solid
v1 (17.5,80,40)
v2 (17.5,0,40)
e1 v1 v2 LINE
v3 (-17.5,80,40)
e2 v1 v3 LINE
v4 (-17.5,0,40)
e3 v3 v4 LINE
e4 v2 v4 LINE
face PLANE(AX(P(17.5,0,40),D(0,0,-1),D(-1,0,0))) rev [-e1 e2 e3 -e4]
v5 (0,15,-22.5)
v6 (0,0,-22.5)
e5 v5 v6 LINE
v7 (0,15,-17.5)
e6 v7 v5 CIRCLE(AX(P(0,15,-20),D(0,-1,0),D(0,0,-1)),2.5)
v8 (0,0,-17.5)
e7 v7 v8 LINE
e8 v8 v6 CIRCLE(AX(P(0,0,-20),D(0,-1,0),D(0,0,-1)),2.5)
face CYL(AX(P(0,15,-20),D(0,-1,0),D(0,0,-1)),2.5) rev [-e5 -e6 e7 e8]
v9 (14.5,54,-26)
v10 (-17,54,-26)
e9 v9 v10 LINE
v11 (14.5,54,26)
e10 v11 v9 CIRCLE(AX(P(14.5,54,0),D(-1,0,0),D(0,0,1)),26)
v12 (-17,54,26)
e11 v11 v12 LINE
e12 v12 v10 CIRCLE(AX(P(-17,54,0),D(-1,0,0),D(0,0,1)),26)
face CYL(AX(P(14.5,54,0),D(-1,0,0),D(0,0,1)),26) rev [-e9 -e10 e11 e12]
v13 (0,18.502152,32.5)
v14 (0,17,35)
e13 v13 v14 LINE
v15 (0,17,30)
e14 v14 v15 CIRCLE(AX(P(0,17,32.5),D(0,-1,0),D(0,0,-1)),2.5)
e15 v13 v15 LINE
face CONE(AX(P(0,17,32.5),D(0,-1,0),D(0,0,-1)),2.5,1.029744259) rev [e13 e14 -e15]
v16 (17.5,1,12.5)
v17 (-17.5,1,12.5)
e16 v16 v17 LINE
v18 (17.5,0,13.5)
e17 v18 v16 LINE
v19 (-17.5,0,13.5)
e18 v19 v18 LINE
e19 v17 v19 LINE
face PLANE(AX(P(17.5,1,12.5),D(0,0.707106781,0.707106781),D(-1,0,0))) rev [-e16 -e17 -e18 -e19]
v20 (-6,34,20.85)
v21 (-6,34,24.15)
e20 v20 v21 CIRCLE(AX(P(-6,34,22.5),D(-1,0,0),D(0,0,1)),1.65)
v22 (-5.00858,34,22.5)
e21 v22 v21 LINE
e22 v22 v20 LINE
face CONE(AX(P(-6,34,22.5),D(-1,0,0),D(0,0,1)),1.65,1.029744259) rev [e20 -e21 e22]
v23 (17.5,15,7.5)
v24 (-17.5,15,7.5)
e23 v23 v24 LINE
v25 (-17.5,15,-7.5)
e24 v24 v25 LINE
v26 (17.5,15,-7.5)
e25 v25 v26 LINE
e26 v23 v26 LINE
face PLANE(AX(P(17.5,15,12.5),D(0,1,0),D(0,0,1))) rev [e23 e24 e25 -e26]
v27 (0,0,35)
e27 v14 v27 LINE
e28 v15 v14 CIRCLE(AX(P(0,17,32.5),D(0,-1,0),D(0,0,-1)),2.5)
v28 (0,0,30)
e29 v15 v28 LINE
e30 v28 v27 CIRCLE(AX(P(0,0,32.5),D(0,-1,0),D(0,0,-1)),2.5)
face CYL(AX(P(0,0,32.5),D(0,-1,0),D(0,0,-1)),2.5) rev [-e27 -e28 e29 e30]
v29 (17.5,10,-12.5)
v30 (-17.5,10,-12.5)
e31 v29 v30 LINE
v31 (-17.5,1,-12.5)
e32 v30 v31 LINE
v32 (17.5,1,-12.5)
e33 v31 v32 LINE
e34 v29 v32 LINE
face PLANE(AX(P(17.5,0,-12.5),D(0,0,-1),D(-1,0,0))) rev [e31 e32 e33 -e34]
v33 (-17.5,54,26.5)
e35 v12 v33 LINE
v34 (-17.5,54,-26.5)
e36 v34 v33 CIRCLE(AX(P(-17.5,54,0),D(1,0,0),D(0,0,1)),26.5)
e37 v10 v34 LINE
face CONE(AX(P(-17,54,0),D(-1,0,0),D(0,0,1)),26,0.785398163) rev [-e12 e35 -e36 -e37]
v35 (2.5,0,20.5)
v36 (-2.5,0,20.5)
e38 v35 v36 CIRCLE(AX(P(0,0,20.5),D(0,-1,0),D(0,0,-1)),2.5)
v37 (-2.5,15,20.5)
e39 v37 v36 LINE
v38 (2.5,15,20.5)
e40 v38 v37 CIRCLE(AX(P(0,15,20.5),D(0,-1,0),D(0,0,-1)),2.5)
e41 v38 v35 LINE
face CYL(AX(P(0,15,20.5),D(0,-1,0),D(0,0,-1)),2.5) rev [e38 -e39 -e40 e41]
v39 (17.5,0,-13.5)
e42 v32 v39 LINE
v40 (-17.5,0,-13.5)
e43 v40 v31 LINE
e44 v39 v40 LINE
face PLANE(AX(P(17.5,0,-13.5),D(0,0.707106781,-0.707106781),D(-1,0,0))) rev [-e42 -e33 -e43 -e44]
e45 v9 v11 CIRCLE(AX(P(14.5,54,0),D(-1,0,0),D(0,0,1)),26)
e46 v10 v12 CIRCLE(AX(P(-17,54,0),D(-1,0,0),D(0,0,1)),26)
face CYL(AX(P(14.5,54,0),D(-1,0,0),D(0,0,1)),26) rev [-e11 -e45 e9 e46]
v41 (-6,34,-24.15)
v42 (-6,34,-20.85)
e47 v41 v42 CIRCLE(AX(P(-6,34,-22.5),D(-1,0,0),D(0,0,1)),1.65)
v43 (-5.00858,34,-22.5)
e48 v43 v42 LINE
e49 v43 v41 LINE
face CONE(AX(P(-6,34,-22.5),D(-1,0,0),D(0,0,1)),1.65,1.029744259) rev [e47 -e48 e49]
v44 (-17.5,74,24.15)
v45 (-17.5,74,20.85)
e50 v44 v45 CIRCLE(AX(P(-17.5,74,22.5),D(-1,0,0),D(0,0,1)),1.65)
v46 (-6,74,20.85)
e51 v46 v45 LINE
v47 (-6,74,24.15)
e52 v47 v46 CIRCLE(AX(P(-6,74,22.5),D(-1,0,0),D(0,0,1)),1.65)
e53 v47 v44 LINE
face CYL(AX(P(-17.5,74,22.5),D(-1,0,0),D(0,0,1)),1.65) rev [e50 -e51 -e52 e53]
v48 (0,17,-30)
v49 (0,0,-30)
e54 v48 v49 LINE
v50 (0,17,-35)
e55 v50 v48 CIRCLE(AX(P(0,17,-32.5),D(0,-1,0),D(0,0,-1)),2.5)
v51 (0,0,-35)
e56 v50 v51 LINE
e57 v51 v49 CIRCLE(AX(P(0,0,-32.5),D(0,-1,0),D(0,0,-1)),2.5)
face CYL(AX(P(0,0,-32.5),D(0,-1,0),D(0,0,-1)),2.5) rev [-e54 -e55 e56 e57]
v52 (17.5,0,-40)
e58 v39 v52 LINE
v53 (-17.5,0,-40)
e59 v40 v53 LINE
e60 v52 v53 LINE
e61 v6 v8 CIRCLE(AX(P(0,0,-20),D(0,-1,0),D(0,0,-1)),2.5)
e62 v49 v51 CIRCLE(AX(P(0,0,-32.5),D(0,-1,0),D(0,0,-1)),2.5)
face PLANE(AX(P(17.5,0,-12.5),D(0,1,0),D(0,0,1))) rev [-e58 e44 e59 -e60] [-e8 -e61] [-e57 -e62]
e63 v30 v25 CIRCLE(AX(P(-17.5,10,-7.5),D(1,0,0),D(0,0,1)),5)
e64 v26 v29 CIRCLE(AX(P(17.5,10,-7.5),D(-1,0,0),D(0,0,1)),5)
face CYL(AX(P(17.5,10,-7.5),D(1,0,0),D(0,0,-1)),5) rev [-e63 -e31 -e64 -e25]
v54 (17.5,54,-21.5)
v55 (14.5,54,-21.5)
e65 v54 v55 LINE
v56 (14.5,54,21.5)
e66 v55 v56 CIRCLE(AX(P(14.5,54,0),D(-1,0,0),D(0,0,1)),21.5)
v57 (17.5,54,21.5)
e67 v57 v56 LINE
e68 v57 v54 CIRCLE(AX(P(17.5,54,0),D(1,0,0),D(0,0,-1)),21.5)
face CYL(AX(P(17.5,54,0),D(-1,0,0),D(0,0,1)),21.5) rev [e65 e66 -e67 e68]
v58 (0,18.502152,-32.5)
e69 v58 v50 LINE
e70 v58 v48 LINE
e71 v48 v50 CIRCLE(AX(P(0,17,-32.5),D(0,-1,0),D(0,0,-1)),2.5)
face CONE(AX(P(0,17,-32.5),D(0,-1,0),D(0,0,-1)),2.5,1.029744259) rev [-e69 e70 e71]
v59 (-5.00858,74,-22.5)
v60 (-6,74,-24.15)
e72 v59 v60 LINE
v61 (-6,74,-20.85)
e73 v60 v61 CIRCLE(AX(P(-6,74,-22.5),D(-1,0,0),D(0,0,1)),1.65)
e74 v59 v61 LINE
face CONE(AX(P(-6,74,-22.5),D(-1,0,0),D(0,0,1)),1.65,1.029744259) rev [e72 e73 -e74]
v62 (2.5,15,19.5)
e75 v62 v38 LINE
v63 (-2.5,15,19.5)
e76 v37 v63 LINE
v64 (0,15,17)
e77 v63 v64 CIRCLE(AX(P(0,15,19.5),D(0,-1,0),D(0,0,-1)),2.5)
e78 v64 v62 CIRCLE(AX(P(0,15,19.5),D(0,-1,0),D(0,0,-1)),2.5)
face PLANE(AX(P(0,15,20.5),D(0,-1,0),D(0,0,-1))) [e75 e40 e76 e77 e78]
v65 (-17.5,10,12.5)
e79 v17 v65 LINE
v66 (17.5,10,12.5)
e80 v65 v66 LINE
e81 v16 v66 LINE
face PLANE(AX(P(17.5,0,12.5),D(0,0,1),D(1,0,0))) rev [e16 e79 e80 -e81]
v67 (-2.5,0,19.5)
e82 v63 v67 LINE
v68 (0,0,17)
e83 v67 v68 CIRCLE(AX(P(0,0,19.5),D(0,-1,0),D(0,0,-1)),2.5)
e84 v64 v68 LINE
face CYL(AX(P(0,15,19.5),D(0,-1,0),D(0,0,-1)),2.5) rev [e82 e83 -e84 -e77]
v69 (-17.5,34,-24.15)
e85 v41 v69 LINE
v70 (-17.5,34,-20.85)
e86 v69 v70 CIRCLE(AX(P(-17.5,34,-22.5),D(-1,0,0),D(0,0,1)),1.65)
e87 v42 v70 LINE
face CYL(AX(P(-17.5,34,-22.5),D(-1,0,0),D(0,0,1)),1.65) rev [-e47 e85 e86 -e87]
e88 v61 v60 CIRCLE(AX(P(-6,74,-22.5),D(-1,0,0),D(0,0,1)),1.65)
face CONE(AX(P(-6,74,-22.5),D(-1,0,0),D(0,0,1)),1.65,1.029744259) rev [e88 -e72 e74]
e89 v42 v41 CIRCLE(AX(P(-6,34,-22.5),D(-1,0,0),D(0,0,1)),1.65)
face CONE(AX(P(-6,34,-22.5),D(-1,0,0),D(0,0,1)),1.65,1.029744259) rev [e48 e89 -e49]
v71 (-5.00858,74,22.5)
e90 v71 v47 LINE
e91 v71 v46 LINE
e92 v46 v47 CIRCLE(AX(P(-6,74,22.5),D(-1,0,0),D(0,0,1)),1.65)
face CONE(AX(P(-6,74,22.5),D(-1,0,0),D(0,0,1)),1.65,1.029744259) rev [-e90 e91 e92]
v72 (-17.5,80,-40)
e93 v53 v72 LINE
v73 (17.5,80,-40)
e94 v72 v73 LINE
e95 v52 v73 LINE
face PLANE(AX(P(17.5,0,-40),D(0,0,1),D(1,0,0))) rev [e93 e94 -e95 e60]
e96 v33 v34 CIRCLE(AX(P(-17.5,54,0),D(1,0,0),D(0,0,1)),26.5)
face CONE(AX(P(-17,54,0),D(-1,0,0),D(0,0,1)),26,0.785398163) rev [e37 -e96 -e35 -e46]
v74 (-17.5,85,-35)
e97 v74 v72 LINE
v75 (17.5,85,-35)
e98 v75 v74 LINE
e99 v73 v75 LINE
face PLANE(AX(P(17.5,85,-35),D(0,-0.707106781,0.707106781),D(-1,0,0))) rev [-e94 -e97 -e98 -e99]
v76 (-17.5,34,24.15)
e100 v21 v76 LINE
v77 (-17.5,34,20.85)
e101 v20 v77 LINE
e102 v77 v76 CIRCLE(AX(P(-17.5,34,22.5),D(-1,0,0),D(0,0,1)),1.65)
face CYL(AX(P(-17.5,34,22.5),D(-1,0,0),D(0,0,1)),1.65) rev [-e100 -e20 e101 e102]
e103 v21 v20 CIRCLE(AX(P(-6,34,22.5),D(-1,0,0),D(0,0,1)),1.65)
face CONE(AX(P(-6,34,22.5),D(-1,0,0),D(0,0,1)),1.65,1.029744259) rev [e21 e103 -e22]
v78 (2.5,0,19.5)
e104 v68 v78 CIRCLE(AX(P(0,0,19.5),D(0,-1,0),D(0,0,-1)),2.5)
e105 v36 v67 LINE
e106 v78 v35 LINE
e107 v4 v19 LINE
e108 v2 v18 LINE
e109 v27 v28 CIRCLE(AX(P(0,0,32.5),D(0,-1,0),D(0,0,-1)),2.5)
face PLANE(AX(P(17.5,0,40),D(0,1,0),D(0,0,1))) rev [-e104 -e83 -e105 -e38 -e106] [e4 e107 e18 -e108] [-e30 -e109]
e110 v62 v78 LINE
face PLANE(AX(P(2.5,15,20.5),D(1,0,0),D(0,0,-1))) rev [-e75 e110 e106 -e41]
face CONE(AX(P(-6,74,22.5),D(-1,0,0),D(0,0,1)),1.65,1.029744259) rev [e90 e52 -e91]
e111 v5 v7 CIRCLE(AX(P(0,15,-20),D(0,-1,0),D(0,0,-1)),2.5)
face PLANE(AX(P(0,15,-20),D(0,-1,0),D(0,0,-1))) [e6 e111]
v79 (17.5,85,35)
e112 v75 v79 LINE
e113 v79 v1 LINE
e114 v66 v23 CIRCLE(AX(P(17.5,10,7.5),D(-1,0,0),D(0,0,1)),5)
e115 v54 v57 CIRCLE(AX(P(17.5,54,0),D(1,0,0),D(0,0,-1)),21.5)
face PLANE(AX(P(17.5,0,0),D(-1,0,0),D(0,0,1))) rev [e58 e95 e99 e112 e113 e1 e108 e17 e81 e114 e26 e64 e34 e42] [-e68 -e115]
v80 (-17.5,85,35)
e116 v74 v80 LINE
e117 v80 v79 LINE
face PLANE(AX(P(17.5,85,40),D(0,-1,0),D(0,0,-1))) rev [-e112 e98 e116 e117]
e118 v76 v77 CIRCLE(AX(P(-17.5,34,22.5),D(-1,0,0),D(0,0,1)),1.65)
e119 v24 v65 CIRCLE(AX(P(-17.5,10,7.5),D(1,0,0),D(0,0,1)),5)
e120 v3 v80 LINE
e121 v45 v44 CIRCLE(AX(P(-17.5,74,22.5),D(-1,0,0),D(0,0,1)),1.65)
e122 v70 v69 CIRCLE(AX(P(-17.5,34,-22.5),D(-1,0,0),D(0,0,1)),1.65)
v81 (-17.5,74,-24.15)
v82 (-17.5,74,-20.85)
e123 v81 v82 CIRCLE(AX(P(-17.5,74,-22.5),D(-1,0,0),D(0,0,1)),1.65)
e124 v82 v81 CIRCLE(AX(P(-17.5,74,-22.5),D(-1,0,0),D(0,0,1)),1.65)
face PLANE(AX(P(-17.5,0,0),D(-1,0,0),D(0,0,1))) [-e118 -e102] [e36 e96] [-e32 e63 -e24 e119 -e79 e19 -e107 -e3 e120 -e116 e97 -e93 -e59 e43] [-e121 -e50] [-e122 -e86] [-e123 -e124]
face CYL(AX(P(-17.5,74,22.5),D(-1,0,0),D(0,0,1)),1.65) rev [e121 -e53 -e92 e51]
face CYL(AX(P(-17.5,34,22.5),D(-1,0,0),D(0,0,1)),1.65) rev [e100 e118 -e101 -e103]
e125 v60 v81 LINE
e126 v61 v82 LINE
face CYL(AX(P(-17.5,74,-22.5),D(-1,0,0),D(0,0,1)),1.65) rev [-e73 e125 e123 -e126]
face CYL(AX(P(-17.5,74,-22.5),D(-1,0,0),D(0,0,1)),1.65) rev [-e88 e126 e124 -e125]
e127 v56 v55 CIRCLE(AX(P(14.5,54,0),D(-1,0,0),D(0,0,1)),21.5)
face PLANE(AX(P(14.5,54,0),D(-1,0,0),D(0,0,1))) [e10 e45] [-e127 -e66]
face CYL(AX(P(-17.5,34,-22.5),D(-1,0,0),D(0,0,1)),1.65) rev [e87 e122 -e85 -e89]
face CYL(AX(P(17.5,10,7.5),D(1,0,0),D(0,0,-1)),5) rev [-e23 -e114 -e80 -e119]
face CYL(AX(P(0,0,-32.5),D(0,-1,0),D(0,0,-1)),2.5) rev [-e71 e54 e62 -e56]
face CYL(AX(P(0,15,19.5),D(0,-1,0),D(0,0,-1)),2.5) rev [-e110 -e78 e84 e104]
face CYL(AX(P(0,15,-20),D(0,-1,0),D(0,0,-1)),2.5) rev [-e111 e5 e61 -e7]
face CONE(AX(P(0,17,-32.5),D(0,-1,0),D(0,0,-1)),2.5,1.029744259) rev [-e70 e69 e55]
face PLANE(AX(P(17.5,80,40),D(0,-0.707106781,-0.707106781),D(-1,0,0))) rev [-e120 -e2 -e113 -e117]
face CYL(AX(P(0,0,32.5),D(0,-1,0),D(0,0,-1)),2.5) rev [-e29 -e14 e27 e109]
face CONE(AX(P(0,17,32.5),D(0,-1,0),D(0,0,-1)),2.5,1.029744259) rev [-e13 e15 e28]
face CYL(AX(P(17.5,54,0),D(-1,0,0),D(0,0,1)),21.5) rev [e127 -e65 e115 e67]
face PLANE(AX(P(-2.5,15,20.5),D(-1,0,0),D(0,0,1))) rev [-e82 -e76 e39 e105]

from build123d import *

# Parameters (mm, degrees)
SKETCH1_R             = 21.5
BOSS_EXTRUDE1_DEPTH   = 17.5
CHAMFER3_SIZE         = 5
FILLET1_R             = 5
M6_TAPPED_HOLE1_D     = 5
M6_TAPPED_HOLE1_DEPTH = 17
M6_TAPPED_HOLE1_TIP   = 1.502151548
SKETCH11_R            = 2.5
CUT_EXTRUDE1_DEPTH    = 15
CHAMFER4_SIZE         = 1
SKETCH12_R            = 26
CUT_EXTRUDE2_DEPTH    = 32
M4_TAPPED_HOLE1_D     = 3.3
M4_TAPPED_HOLE1_DEPTH = 11.5
M4_TAPPED_HOLE1_TIP   = 0.991420021
CHAMFER5_SIZE         = 0.5


with BuildPart() as part:
    # Sketch1 → Boss-Extrude1 (new, symmetric)
    with BuildSketch(Plane(origin=(0, 0, 0), x_dir=(0, 0, -1), z_dir=(1, 0, 0))):
        Polygon((-40, 85), (40, 85), (40, 0), (12.5, 0), (12.5, 15), (-12.5, 15), (-12.5, 0), (-40, 0), align=None)
        with Locations((0, 54)):
            Circle(SKETCH1_R, mode=Mode.SUBTRACT)
    extrude(amount=BOSS_EXTRUDE1_DEPTH, both=True)

    # Chamfer3
    chamfer3_edges = [part.edges().sort_by_distance(p)[0] for p in [
        (0, 85, 40),
        (0, 85, -40),
    ]]
    chamfer(chamfer3_edges, length=CHAMFER3_SIZE)

    # Fillet1
    fillet1_edges = [part.edges().sort_by_distance(p)[0] for p in [
        (0, 15, -12.5),
        (0, 15, 12.5),
    ]]
    fillet(fillet1_edges, radius=FILLET1_R)

    # M6 Tapped Hole1
    with Locations(Plane(origin=(0, 0, 0), x_dir=(-1, 0, 0), z_dir=(0, -1, 0))):
        with Locations((0, -32.5), (0, 32.5)):
            Hole(M6_TAPPED_HOLE1_D / 2, depth=M6_TAPPED_HOLE1_DEPTH)
            with Locations((0, 0, -(M6_TAPPED_HOLE1_DEPTH + M6_TAPPED_HOLE1_TIP / 2))):  # 118° drill point
                Cone(0, M6_TAPPED_HOLE1_D / 2, M6_TAPPED_HOLE1_TIP, mode=Mode.SUBTRACT)

    # Sketch11 → Cut-Extrude1 (cut)
    with BuildSketch(Plane.XZ):
        with Locations(Location((0, -20, 0), (0, 0, 270))):
            Circle(SKETCH11_R)
        with BuildLine():
            Line((2.5, 20.5), (2.5, 19.5))
            ThreePointArc((2.5, 19.5), (0, 17), (-2.5, 19.5))
            Line((-2.5, 19.5), (-2.5, 20.5))
            ThreePointArc((-2.5, 20.5), (0, 23), (2.5, 20.5))
        make_face()
    extrude(amount=-CUT_EXTRUDE1_DEPTH, mode=Mode.SUBTRACT)

    # Chamfer4
    chamfer4_edges = [part.edges().sort_by_distance(p)[0] for p in [
        (0, 0, -12.5),
        (0, 0, 12.5),
    ]]
    chamfer(chamfer4_edges, length=CHAMFER4_SIZE)

    # Sketch12 → Cut-Extrude2 (cut)
    with BuildSketch(Plane.ZY.offset(17.5)):
        with Locations((0, 54)):
            Circle(SKETCH12_R)
    extrude(amount=-CUT_EXTRUDE2_DEPTH, mode=Mode.SUBTRACT)

    # M4 Tapped Hole1
    with Locations(Plane.ZY.offset(17.5)):
        with Locations((-22.5, 74), (22.5, 74), (22.5, 34), (-22.5, 34)):
            Hole(M4_TAPPED_HOLE1_D / 2, depth=M4_TAPPED_HOLE1_DEPTH)
            with Locations((0, 0, -(M4_TAPPED_HOLE1_DEPTH + M4_TAPPED_HOLE1_TIP / 2))):  # 118° drill point
                Cone(0, M4_TAPPED_HOLE1_D / 2, M4_TAPPED_HOLE1_TIP, mode=Mode.SUBTRACT)

    # Chamfer5
    chamfer5_edges = [part.edges().sort_by_distance(p)[0] for p in [
        (-17.5, 54, -26),
    ]]
    chamfer(chamfer5_edges, length=CHAMFER5_SIZE)


solid = part.part
